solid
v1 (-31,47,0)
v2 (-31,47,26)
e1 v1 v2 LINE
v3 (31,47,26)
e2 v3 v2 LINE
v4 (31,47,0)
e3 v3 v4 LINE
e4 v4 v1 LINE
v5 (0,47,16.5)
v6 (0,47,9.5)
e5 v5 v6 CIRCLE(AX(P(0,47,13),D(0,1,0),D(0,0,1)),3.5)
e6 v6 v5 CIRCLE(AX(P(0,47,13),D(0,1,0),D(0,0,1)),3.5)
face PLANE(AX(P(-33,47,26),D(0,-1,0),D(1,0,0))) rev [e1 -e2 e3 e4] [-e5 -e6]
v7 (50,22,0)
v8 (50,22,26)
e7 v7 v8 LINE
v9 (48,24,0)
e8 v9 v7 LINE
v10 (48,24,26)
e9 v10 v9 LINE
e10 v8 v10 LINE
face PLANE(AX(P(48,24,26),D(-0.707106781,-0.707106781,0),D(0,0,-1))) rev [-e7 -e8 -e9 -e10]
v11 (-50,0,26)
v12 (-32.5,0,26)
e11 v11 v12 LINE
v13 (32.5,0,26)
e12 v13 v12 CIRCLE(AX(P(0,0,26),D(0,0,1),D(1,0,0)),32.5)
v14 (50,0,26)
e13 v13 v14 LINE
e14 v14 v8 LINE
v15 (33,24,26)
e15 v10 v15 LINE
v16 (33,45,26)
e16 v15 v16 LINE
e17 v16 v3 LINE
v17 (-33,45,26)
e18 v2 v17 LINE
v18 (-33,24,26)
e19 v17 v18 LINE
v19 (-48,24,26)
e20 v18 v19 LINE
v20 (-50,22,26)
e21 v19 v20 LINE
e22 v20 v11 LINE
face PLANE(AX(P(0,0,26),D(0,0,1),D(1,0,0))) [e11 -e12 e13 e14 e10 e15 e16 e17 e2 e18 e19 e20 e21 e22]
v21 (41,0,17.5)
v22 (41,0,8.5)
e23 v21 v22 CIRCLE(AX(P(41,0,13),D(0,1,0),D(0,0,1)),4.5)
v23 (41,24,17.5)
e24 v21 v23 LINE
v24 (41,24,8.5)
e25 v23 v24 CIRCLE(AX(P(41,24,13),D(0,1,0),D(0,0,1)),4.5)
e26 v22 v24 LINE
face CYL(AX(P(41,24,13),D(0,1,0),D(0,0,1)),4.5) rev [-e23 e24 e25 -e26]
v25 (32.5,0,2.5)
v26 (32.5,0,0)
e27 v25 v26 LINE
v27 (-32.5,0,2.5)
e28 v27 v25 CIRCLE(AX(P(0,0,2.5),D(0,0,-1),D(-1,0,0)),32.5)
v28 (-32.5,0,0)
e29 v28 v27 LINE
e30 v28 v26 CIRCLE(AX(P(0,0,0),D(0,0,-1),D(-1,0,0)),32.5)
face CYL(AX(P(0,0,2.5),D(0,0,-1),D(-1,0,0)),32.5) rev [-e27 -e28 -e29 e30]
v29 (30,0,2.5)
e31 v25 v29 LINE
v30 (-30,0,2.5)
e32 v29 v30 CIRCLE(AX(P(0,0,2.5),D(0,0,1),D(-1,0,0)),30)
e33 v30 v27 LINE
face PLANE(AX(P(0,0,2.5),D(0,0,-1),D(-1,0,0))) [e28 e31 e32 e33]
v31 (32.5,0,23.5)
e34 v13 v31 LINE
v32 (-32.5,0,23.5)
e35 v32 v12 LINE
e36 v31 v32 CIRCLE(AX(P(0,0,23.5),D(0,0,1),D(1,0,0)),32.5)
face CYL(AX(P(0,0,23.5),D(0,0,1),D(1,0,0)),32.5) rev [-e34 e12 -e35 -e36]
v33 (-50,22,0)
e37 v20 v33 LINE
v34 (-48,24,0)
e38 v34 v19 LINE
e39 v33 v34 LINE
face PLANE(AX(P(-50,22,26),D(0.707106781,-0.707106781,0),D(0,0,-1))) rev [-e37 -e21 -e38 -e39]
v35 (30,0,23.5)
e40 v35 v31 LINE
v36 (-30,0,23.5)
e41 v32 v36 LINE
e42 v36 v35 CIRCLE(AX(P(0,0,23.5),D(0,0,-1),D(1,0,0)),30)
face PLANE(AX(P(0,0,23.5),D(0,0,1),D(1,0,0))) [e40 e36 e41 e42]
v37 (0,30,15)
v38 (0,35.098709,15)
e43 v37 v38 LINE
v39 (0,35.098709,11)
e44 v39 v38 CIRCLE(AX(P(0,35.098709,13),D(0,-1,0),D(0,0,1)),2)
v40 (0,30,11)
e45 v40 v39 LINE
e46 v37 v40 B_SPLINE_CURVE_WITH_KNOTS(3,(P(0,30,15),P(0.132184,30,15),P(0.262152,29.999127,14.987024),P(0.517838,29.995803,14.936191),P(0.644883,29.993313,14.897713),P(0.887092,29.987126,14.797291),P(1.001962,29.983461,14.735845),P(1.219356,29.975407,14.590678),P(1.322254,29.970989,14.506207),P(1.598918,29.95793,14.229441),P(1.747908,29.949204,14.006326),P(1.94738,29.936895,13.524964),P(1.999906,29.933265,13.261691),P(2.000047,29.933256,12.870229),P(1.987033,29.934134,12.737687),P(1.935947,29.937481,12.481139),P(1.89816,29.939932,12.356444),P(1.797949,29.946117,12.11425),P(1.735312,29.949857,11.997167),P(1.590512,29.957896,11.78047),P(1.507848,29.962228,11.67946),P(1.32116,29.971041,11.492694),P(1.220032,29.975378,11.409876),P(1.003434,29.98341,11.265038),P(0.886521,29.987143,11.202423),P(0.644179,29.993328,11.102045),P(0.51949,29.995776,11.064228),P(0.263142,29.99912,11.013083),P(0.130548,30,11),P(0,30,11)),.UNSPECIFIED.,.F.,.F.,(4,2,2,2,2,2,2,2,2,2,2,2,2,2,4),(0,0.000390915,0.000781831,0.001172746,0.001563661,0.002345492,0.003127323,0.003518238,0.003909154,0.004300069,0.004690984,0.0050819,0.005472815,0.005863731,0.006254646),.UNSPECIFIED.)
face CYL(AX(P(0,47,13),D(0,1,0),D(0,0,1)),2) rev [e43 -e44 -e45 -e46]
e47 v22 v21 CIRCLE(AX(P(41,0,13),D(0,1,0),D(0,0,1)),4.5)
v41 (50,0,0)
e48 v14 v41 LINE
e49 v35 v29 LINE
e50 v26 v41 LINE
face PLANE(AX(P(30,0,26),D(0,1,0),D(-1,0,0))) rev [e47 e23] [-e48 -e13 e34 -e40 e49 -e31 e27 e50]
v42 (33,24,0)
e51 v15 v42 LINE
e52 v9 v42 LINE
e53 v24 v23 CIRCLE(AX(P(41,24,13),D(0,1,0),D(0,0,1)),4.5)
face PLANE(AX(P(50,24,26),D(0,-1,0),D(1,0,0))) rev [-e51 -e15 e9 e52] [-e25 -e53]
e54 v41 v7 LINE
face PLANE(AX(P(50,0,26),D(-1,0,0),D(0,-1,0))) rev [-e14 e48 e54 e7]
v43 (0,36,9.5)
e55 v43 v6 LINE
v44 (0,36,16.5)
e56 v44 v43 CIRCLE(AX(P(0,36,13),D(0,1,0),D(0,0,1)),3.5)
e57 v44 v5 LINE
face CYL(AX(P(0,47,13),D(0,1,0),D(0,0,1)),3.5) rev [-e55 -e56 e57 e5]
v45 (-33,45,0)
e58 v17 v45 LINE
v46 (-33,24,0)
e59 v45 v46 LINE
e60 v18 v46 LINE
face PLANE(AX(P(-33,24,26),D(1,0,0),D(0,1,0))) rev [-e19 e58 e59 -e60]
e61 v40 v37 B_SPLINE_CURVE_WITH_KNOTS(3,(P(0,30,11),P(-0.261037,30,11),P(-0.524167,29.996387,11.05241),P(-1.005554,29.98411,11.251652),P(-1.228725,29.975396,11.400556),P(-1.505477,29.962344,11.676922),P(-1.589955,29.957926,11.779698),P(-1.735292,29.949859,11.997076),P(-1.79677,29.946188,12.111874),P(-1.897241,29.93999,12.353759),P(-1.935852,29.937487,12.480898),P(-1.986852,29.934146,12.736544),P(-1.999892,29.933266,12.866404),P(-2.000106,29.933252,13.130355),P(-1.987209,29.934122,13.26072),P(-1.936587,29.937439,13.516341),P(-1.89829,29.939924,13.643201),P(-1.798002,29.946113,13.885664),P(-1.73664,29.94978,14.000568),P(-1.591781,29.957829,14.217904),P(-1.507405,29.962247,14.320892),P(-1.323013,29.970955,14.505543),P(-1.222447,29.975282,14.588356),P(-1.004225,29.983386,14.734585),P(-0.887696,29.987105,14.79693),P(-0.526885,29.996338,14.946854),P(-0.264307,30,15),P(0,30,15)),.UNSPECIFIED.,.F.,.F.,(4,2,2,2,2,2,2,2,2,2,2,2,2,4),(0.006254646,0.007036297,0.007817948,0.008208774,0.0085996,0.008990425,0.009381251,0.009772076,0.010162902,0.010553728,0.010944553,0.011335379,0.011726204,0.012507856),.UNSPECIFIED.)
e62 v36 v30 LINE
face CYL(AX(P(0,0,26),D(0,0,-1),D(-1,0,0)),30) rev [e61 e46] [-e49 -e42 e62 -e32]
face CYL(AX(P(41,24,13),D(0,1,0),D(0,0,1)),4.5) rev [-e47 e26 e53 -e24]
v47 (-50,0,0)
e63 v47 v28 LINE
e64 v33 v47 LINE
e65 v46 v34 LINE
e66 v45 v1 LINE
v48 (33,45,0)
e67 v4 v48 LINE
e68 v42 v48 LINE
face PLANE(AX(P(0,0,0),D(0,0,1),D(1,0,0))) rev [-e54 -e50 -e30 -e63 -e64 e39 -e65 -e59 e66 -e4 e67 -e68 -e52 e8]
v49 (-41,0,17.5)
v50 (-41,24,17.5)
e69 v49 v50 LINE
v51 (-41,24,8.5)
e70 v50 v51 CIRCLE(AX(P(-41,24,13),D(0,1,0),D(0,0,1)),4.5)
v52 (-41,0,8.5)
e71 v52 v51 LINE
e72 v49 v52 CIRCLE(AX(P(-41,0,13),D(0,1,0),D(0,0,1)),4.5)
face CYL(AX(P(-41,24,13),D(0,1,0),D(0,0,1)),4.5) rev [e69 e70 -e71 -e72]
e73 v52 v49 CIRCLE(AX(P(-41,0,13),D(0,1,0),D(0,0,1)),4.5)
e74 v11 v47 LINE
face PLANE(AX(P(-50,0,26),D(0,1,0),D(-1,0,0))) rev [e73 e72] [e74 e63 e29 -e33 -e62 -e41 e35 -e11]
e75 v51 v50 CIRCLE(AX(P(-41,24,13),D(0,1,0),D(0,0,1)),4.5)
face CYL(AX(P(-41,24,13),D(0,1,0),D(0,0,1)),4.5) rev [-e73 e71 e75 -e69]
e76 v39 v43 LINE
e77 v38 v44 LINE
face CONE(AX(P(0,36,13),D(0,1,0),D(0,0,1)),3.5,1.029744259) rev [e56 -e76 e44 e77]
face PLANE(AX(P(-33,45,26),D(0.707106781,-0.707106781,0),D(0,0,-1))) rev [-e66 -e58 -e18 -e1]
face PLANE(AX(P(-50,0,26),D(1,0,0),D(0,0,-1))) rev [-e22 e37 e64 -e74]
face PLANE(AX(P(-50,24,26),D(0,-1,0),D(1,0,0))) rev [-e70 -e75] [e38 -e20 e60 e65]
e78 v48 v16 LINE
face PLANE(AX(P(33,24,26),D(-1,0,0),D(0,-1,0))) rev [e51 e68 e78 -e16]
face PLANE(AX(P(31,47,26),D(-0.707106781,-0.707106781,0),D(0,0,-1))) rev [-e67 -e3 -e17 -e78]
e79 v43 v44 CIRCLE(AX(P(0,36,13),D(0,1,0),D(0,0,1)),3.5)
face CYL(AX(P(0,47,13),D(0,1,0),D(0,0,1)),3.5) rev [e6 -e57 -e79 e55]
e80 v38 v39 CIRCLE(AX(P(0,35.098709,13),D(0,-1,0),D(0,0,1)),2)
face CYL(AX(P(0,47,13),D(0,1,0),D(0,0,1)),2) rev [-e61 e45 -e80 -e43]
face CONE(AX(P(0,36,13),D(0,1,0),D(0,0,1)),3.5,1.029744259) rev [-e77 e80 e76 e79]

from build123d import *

# Parameters (mm, degrees)
BOSS_EXTRUDE1_DEPTH       = 26
CHAMFER1_SIZE             = 2
M8X1_0_TAPPED_HOLE1_D     = 7
M8X1_0_TAPPED_HOLE1_DEPTH = 11
M8X1_0_TAPPED_HOLE1_TIP   = 2.103012167
HOLE2_D                   = 9
SKETCH11_R                = 32.5
CUT_EXTRUDE1_DEPTH        = 2.5
CUT_EXTRUDE2_START        = -2.5
SKETCH12_R                = 32.5
CUT_EXTRUDE2_DEPTH        = 2.5
HOLE3_D                   = 4


with BuildPart() as part:
    # Sketch1 → Boss-Extrude1 (new body)
    with BuildSketch(Plane.XY):
        with BuildLine():
            Line((-50, 24), (-33, 24))
            Line((-33, 24), (-33, 47))
            Line((-33, 47), (33, 47))
            Line((33, 47), (33, 24))
            Line((33, 24), (50, 24))
            Line((50, 24), (50, 0))
            Line((50, 0), (30, 0))
            ThreePointArc((30, 0), (0, 30), (-30, 0))
            Line((-30, 0), (-50, 0))
            Line((-50, 0), (-50, 24))
        make_face()
    extrude(amount=BOSS_EXTRUDE1_DEPTH)

    # Chamfer1
    chamfer1_edges = [part.edges().sort_by_distance(p)[0] for p in [
        (-50, 24, 13),
        (-33, 47, 13),
        (33, 47, 13),
        (50, 24, 13),
    ]]
    chamfer(chamfer1_edges, length=CHAMFER1_SIZE)

    # M8x1.0 Tapped Hole1
    with Locations(Plane(origin=(0, 47, 0), x_dir=(1, 0, 0), z_dir=(0, 1, 0))):
        with Locations((0, -13)):
            Hole(M8X1_0_TAPPED_HOLE1_D / 2, depth=M8X1_0_TAPPED_HOLE1_DEPTH)
            with Locations((0, 0, -(M8X1_0_TAPPED_HOLE1_DEPTH + M8X1_0_TAPPED_HOLE1_TIP / 2))):  # 118° drill point
                Cone(0, M8X1_0_TAPPED_HOLE1_D / 2, M8X1_0_TAPPED_HOLE1_TIP, mode=Mode.SUBTRACT)

    # Hole2 (through all)
    with Locations(Plane(origin=(0, 24, 0), x_dir=(1, 0, 0), z_dir=(0, 1, 0))):
        with Locations((-41, -13), (41, -13)):
            Hole(HOLE2_D / 2)

    # Sketch11 → Cut-Extrude1 (cut)
    with BuildSketch(Plane.XY.offset(26)):
        Circle(SKETCH11_R)
    extrude(amount=-CUT_EXTRUDE1_DEPTH, mode=Mode.SUBTRACT)

    # Sketch12 → Cut-Extrude2 (cut)
    with BuildSketch(Plane(origin=(0, 0, 0), x_dir=(-1, 0, 0), z_dir=(0, 0, -1)).offset(CUT_EXTRUDE2_START)):
        Circle(SKETCH12_R)
    extrude(amount=CUT_EXTRUDE2_DEPTH, mode=Mode.SUBTRACT)

    # Hole3 (through all)
    with Locations(Plane(origin=(0, 47, 0), x_dir=(1, 0, 0), z_dir=(0, 1, 0))):
        with Locations((0, -13)):
            Hole(HOLE3_D / 2)


solid = part.part
